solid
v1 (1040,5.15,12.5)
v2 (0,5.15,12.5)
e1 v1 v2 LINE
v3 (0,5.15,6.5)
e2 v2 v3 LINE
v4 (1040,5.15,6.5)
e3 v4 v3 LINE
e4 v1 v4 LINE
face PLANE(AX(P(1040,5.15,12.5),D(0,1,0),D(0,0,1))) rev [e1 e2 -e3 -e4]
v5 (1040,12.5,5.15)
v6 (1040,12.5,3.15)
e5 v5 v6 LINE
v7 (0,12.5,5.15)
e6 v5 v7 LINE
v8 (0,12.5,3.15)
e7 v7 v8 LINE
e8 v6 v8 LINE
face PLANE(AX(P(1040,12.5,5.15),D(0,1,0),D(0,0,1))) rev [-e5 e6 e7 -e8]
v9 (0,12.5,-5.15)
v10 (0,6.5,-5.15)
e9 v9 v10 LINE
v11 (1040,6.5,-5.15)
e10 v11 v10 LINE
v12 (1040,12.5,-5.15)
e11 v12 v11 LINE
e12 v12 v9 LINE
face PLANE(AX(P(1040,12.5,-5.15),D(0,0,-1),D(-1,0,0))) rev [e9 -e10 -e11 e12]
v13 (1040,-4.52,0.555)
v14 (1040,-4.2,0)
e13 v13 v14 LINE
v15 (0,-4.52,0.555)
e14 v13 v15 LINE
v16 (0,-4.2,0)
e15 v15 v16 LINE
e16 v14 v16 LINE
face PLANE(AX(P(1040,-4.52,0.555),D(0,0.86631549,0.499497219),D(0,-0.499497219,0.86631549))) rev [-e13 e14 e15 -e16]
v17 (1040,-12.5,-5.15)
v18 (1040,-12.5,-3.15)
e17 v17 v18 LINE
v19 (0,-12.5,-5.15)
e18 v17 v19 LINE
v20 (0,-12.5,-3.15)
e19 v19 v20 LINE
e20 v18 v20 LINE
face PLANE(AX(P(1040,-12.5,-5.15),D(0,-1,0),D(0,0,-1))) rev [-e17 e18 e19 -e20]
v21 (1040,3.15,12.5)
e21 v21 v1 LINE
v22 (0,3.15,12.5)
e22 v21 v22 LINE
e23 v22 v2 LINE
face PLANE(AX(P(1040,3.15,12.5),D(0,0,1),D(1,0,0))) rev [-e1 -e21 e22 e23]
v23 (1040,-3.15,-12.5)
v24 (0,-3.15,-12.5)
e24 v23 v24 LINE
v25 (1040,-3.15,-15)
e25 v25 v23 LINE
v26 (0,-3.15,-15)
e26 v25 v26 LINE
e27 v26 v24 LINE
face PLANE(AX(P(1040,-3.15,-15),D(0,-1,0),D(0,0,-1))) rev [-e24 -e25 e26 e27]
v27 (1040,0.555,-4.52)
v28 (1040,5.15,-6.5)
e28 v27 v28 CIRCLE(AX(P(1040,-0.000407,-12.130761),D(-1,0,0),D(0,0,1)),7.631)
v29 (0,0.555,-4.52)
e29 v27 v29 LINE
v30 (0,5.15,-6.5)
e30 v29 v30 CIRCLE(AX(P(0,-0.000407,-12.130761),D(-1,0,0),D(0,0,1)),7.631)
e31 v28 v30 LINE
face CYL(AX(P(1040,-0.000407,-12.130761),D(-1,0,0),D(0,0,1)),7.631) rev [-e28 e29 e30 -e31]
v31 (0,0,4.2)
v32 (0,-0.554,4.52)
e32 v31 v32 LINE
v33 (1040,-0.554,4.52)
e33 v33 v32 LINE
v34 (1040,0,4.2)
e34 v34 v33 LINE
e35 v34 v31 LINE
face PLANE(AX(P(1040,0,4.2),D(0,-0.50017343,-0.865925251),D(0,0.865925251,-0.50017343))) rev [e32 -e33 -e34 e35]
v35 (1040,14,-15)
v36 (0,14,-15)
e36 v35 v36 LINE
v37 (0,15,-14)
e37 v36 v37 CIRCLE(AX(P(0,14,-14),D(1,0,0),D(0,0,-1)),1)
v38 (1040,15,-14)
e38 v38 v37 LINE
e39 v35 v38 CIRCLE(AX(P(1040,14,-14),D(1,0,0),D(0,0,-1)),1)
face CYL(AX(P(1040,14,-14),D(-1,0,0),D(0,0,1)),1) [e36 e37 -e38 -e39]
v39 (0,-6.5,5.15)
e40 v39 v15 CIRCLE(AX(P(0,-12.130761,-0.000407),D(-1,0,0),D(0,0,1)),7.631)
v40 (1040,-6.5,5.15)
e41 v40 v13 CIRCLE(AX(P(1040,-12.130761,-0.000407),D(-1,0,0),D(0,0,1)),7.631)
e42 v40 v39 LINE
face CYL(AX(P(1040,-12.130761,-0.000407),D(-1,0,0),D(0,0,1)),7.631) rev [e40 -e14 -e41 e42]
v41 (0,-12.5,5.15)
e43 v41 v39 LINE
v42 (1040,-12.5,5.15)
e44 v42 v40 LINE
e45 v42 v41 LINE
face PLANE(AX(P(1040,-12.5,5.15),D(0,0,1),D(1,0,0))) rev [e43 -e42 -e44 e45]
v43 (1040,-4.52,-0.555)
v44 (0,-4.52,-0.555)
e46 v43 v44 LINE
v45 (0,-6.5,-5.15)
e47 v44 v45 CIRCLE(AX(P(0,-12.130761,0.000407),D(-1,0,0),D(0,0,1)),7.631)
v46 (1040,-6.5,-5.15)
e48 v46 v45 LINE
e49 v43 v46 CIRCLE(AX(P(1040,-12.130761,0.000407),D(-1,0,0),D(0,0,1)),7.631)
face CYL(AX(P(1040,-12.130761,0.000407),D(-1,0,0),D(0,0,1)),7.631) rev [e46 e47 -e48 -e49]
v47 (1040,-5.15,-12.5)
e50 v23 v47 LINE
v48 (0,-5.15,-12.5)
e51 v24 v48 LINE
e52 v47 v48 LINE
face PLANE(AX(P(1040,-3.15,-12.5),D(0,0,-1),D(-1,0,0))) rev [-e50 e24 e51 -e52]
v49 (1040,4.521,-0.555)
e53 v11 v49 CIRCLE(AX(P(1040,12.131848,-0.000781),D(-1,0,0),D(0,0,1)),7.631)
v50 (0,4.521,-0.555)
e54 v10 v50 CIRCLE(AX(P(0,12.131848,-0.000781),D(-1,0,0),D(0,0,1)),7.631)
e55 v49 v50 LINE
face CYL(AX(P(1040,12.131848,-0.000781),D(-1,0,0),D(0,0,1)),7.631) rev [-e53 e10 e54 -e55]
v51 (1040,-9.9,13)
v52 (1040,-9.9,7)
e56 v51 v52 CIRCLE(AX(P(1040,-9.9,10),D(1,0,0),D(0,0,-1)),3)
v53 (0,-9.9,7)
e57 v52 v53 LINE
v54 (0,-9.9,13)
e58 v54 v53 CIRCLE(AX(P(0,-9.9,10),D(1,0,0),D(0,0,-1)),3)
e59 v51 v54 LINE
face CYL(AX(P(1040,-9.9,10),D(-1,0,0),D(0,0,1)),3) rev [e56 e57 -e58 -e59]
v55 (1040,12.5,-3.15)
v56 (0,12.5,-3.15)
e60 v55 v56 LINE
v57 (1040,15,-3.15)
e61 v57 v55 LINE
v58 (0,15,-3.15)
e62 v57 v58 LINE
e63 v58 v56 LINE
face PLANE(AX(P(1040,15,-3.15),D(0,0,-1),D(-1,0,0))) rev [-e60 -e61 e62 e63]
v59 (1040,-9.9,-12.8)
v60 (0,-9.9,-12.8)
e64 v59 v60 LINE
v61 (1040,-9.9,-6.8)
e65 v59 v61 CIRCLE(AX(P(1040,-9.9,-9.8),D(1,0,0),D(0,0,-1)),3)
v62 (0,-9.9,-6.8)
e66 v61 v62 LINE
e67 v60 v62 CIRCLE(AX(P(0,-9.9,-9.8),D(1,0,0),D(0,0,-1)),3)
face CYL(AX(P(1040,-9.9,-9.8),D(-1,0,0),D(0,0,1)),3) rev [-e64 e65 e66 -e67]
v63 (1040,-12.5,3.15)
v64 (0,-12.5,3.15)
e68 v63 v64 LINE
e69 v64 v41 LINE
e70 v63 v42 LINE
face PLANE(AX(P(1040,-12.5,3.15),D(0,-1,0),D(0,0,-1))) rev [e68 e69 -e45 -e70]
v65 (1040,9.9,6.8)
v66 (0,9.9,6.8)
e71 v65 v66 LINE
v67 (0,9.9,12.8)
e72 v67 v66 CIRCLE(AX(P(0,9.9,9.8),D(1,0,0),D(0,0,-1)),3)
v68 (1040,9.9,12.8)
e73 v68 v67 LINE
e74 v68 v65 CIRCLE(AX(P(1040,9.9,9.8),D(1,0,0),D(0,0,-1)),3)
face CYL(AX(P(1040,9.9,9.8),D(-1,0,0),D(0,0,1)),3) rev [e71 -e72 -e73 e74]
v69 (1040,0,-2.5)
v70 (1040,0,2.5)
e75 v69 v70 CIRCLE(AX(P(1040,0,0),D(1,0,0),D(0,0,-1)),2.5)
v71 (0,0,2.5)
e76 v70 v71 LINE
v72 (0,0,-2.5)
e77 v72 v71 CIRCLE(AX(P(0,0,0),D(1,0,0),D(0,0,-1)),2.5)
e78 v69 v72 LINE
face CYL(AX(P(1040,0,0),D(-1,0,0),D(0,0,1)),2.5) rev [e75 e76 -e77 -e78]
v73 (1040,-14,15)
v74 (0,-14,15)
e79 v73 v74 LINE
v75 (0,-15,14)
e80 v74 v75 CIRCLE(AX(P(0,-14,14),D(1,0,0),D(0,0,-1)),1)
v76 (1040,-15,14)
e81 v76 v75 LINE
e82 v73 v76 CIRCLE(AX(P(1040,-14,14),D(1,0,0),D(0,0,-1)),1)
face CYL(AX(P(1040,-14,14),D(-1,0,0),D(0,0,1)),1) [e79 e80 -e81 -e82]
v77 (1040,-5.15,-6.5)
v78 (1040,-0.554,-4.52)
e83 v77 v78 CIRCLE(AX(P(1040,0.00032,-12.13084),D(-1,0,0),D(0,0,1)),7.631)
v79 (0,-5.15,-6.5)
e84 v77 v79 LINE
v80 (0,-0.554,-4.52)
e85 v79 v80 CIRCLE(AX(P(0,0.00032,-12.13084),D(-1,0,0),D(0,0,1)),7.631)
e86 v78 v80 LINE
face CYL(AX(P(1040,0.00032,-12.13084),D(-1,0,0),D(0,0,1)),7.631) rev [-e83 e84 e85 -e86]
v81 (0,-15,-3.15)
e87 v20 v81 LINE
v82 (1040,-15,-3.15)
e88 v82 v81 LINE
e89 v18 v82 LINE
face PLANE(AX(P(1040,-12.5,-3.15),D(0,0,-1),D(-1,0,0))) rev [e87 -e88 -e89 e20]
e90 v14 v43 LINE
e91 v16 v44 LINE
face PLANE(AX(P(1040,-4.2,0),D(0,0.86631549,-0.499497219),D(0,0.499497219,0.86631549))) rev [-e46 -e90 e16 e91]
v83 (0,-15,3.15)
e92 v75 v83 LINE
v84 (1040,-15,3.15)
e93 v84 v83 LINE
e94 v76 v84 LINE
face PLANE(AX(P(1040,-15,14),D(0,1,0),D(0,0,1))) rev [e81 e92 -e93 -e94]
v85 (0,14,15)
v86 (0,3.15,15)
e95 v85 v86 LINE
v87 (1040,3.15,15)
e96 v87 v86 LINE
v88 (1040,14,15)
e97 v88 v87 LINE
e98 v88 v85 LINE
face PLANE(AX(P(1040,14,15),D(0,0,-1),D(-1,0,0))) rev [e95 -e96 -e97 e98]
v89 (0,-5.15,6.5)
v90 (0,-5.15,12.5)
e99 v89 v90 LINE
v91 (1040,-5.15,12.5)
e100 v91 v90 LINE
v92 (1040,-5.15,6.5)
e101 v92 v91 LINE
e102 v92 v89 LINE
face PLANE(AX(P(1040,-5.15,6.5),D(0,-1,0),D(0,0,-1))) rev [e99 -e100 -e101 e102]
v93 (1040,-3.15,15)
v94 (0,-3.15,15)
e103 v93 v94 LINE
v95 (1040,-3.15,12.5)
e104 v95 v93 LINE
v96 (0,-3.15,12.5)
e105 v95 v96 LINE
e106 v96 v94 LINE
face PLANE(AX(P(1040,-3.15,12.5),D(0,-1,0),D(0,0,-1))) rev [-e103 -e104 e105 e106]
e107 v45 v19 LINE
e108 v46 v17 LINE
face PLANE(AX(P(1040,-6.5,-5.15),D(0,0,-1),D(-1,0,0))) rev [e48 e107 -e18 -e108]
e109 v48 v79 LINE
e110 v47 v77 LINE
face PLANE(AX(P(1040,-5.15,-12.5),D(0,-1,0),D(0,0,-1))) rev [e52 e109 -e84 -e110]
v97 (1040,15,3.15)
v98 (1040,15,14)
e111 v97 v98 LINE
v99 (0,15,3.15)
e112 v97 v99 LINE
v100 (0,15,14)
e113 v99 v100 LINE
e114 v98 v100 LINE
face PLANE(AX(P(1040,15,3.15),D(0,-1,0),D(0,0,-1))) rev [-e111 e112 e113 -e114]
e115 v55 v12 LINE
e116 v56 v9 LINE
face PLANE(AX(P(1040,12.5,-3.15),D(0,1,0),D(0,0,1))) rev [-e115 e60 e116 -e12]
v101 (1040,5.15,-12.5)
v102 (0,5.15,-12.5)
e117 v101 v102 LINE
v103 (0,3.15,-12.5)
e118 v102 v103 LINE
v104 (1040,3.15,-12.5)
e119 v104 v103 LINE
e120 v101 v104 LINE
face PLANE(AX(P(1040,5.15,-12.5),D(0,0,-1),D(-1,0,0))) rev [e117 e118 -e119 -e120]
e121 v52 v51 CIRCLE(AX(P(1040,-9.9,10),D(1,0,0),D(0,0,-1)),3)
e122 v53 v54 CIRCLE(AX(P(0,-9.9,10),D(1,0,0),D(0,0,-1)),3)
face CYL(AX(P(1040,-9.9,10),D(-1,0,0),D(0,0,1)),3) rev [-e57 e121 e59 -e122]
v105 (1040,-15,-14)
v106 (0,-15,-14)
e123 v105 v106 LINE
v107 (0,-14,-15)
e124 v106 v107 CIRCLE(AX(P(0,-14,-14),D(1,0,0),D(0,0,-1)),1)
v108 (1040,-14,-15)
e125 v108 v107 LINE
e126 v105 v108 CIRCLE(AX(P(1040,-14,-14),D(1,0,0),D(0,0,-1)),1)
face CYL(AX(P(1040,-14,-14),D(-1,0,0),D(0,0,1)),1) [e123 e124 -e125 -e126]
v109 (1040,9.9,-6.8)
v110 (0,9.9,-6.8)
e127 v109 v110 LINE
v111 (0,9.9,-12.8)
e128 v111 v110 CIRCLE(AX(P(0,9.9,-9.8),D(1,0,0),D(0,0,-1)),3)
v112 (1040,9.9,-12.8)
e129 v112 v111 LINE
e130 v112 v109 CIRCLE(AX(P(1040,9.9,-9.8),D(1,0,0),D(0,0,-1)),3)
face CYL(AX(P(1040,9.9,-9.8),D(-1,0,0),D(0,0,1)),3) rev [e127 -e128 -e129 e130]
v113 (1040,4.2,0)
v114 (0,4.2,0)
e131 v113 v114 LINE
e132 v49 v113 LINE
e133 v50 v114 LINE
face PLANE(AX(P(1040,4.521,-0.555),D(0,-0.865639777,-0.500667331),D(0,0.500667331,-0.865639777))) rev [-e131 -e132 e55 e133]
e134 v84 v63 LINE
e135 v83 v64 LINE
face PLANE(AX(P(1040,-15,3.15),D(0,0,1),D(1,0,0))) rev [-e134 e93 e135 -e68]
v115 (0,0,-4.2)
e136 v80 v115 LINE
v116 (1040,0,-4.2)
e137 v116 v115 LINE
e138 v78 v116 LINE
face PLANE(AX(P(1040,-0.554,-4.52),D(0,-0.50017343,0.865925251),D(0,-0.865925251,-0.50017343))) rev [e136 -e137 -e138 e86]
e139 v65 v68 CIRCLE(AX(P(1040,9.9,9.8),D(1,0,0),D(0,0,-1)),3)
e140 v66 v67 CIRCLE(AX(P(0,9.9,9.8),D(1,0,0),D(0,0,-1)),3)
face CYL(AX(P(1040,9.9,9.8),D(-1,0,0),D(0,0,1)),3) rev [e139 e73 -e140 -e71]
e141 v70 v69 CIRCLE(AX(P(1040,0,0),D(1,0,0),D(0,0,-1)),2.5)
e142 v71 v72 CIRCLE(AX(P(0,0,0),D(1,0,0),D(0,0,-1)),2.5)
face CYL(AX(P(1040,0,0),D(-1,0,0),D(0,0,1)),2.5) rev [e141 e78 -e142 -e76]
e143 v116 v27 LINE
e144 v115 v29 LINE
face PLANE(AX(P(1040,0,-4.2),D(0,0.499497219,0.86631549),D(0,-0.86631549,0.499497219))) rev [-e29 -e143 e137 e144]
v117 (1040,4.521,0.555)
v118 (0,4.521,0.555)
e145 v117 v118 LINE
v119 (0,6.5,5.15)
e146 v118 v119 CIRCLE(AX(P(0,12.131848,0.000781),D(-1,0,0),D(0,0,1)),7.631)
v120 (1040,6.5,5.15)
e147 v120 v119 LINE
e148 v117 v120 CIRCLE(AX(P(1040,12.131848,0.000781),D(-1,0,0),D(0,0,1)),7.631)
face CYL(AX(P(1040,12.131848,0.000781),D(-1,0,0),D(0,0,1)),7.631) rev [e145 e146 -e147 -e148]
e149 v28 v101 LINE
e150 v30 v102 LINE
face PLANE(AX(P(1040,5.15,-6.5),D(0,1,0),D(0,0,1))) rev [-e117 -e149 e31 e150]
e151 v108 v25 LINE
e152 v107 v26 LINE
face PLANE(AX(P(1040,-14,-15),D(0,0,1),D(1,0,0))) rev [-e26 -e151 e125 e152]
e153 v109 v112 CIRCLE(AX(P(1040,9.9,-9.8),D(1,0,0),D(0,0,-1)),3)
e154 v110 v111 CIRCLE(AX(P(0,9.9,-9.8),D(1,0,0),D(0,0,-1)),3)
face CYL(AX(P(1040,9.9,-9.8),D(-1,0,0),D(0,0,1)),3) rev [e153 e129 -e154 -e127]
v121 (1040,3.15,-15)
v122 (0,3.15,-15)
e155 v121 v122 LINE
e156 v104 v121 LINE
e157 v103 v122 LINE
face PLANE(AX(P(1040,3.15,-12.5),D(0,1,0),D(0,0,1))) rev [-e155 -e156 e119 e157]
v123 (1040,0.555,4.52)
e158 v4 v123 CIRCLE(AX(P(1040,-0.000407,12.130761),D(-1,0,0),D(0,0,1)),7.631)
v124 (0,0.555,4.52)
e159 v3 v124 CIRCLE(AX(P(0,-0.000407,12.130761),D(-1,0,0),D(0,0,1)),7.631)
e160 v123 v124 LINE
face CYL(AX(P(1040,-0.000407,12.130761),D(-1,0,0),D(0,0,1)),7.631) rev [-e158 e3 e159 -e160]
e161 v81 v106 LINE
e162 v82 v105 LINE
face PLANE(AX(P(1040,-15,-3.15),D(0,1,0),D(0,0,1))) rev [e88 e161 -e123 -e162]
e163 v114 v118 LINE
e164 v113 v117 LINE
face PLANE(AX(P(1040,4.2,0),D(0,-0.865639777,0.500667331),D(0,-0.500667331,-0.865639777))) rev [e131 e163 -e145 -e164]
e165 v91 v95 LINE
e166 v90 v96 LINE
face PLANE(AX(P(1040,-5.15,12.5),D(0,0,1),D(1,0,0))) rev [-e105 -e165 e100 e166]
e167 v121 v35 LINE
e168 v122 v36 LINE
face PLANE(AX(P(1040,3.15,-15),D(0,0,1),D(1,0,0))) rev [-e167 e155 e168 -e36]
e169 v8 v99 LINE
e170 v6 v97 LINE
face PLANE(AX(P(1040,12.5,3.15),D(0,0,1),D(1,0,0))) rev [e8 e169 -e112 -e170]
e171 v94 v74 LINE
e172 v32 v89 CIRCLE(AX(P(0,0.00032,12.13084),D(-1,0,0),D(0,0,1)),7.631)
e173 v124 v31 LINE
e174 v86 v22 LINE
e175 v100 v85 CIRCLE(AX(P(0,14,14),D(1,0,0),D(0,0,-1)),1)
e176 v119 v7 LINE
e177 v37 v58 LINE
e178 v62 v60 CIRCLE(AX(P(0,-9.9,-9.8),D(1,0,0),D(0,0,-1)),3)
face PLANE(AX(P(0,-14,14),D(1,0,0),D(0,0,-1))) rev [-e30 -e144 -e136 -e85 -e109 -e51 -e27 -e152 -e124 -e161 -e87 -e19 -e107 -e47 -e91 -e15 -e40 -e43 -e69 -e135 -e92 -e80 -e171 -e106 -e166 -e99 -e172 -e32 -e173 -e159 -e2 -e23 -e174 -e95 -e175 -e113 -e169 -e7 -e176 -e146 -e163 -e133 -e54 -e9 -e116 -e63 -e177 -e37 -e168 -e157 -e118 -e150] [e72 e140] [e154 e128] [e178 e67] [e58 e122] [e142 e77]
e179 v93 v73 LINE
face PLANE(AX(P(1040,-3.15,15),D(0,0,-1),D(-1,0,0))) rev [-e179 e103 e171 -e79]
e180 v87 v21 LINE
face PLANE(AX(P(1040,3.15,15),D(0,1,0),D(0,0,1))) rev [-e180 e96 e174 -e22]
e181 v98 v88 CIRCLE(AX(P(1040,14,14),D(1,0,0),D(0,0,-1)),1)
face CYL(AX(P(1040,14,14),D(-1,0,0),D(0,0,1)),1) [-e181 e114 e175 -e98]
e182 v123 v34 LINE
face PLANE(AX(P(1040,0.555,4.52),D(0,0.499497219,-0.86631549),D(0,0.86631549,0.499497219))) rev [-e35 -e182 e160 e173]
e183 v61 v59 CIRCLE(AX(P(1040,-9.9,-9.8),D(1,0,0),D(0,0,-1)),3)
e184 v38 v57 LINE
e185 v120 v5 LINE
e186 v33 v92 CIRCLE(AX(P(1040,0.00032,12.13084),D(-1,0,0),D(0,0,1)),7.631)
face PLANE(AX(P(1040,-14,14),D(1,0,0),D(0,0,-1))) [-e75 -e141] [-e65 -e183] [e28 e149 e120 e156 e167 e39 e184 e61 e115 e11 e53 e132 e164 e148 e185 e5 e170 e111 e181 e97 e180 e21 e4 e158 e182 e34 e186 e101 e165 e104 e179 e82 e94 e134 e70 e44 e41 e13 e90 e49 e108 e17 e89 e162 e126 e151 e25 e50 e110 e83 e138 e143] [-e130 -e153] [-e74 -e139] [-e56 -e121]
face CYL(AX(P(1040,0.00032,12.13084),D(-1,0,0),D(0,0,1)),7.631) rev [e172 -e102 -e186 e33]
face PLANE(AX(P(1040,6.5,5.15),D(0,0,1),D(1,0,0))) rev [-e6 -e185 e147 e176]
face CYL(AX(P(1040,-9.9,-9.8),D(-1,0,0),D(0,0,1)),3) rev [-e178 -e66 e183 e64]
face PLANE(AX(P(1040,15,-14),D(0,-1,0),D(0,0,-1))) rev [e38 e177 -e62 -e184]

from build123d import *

# Parameters (mm, degrees)
SKETCH_11_R         = 3
SKETCH_11_R_2       = 2.5
F_0_GY_3030_1_DEPTH = 1040


with BuildPart() as part:
    # 草图11 → 0国耀铝型材 GY-3030国标铝型材(1) (new body)
    with BuildSketch(Plane(origin=(0, 0, 0), x_dir=(0, 0, -1), z_dir=(1, 0, 0))):
        with BuildLine():
            Line((-14, -15), (-3.15, -15))
            Line((-3.15, -15), (-3.15, -12.5))
            Line((-3.15, -12.5), (-5.15, -12.5))
            Line((-5.15, -12.5), (-5.15, -6.5))
            ThreePointArc((-5.15, -6.5), (-3.019390742, -5.122695475), (-0.555, -4.52))
            Line((-0.555, -4.52), (0, -4.2))
            Line((0, -4.2), (0.555, -4.52))
            ThreePointArc((0.555, -4.52), (3.019390742, -5.122695475), (5.15, -6.5))
            Line((5.15, -6.5), (5.15, -12.5))
            Line((5.15, -12.5), (3.15, -12.5))
            Line((3.15, -12.5), (3.15, -15))
            Line((3.15, -15), (14, -15))
            ThreePointArc((14, -15), (14.707106781, -14.707106781), (15, -14))
            Line((15, -14), (15, -3.15))
            Line((15, -3.15), (12.5, -3.15))
            Line((12.5, -3.15), (12.5, -5.15))
            Line((12.5, -5.15), (6.5, -5.15))
            ThreePointArc((6.5, -5.15), (5.12253592, -3.018923167), (4.52, -0.554))
            Line((4.52, -0.554), (4.2, 0))
            Line((4.2, 0), (4.52, 0.555))
            ThreePointArc((4.52, 0.555), (5.122695475, 3.019390742), (6.5, 5.15))
            Line((6.5, 5.15), (12.5, 5.15))
            Line((12.5, 5.15), (12.5, 3.15))
            Line((12.5, 3.15), (15, 3.15))
            Line((15, 3.15), (15, 14))
            ThreePointArc((15, 14), (14.707106781, 14.707106781), (14, 15))
            Line((14, 15), (3.15, 15))
            Line((3.15, 15), (3.15, 12.5))
            Line((3.15, 12.5), (5.15, 12.5))
            Line((5.15, 12.5), (5.15, 6.5))
            ThreePointArc((5.15, 6.5), (3.019292492, 5.123227892), (0.555, 4.521))
            Line((0.555, 4.521), (0, 4.2))
            Line((0, 4.2), (-0.555, 4.521))
            ThreePointArc((-0.555, 4.521), (-3.019292492, 5.123227892), (-5.15, 6.5))
            Line((-5.15, 6.5), (-5.15, 12.5))
            Line((-5.15, 12.5), (-3.15, 12.5))
            Line((-3.15, 12.5), (-3.15, 15))
            Line((-3.15, 15), (-14, 15))
            ThreePointArc((-14, 15), (-14.707106781, 14.707106781), (-15, 14))
            Line((-15, 14), (-15, 3.15))
            Line((-15, 3.15), (-12.5, 3.15))
            Line((-12.5, 3.15), (-12.5, 5.15))
            Line((-12.5, 5.15), (-6.5, 5.15))
            ThreePointArc((-6.5, 5.15), (-5.122695475, 3.019390742), (-4.52, 0.555))
            Line((-4.52, 0.555), (-4.2, 0))
            Line((-4.2, 0), (-4.52, -0.554))
            ThreePointArc((-4.52, -0.554), (-5.12253592, -3.018923167), (-6.5, -5.15))
            Line((-6.5, -5.15), (-12.5, -5.15))
            Line((-12.5, -5.15), (-12.5, -3.15))
            Line((-12.5, -3.15), (-15, -3.15))
            Line((-15, -3.15), (-15, -14))
            ThreePointArc((-15, -14), (-14.707106781, -14.707106781), (-14, -15))
        make_face()
        with Locations((9.8, 9.9)):
            Circle(SKETCH_11_R, mode=Mode.SUBTRACT)
        with Locations((9.8, -9.9)):
            Circle(SKETCH_11_R, mode=Mode.SUBTRACT)
        Circle(SKETCH_11_R_2, mode=Mode.SUBTRACT)
        with Locations((-9.8, 9.9)):
            Circle(SKETCH_11_R, mode=Mode.SUBTRACT)
        with Locations((-10, -9.9)):
            Circle(SKETCH_11_R, mode=Mode.SUBTRACT)
    extrude(amount=F_0_GY_3030_1_DEPTH)


solid = part.part
